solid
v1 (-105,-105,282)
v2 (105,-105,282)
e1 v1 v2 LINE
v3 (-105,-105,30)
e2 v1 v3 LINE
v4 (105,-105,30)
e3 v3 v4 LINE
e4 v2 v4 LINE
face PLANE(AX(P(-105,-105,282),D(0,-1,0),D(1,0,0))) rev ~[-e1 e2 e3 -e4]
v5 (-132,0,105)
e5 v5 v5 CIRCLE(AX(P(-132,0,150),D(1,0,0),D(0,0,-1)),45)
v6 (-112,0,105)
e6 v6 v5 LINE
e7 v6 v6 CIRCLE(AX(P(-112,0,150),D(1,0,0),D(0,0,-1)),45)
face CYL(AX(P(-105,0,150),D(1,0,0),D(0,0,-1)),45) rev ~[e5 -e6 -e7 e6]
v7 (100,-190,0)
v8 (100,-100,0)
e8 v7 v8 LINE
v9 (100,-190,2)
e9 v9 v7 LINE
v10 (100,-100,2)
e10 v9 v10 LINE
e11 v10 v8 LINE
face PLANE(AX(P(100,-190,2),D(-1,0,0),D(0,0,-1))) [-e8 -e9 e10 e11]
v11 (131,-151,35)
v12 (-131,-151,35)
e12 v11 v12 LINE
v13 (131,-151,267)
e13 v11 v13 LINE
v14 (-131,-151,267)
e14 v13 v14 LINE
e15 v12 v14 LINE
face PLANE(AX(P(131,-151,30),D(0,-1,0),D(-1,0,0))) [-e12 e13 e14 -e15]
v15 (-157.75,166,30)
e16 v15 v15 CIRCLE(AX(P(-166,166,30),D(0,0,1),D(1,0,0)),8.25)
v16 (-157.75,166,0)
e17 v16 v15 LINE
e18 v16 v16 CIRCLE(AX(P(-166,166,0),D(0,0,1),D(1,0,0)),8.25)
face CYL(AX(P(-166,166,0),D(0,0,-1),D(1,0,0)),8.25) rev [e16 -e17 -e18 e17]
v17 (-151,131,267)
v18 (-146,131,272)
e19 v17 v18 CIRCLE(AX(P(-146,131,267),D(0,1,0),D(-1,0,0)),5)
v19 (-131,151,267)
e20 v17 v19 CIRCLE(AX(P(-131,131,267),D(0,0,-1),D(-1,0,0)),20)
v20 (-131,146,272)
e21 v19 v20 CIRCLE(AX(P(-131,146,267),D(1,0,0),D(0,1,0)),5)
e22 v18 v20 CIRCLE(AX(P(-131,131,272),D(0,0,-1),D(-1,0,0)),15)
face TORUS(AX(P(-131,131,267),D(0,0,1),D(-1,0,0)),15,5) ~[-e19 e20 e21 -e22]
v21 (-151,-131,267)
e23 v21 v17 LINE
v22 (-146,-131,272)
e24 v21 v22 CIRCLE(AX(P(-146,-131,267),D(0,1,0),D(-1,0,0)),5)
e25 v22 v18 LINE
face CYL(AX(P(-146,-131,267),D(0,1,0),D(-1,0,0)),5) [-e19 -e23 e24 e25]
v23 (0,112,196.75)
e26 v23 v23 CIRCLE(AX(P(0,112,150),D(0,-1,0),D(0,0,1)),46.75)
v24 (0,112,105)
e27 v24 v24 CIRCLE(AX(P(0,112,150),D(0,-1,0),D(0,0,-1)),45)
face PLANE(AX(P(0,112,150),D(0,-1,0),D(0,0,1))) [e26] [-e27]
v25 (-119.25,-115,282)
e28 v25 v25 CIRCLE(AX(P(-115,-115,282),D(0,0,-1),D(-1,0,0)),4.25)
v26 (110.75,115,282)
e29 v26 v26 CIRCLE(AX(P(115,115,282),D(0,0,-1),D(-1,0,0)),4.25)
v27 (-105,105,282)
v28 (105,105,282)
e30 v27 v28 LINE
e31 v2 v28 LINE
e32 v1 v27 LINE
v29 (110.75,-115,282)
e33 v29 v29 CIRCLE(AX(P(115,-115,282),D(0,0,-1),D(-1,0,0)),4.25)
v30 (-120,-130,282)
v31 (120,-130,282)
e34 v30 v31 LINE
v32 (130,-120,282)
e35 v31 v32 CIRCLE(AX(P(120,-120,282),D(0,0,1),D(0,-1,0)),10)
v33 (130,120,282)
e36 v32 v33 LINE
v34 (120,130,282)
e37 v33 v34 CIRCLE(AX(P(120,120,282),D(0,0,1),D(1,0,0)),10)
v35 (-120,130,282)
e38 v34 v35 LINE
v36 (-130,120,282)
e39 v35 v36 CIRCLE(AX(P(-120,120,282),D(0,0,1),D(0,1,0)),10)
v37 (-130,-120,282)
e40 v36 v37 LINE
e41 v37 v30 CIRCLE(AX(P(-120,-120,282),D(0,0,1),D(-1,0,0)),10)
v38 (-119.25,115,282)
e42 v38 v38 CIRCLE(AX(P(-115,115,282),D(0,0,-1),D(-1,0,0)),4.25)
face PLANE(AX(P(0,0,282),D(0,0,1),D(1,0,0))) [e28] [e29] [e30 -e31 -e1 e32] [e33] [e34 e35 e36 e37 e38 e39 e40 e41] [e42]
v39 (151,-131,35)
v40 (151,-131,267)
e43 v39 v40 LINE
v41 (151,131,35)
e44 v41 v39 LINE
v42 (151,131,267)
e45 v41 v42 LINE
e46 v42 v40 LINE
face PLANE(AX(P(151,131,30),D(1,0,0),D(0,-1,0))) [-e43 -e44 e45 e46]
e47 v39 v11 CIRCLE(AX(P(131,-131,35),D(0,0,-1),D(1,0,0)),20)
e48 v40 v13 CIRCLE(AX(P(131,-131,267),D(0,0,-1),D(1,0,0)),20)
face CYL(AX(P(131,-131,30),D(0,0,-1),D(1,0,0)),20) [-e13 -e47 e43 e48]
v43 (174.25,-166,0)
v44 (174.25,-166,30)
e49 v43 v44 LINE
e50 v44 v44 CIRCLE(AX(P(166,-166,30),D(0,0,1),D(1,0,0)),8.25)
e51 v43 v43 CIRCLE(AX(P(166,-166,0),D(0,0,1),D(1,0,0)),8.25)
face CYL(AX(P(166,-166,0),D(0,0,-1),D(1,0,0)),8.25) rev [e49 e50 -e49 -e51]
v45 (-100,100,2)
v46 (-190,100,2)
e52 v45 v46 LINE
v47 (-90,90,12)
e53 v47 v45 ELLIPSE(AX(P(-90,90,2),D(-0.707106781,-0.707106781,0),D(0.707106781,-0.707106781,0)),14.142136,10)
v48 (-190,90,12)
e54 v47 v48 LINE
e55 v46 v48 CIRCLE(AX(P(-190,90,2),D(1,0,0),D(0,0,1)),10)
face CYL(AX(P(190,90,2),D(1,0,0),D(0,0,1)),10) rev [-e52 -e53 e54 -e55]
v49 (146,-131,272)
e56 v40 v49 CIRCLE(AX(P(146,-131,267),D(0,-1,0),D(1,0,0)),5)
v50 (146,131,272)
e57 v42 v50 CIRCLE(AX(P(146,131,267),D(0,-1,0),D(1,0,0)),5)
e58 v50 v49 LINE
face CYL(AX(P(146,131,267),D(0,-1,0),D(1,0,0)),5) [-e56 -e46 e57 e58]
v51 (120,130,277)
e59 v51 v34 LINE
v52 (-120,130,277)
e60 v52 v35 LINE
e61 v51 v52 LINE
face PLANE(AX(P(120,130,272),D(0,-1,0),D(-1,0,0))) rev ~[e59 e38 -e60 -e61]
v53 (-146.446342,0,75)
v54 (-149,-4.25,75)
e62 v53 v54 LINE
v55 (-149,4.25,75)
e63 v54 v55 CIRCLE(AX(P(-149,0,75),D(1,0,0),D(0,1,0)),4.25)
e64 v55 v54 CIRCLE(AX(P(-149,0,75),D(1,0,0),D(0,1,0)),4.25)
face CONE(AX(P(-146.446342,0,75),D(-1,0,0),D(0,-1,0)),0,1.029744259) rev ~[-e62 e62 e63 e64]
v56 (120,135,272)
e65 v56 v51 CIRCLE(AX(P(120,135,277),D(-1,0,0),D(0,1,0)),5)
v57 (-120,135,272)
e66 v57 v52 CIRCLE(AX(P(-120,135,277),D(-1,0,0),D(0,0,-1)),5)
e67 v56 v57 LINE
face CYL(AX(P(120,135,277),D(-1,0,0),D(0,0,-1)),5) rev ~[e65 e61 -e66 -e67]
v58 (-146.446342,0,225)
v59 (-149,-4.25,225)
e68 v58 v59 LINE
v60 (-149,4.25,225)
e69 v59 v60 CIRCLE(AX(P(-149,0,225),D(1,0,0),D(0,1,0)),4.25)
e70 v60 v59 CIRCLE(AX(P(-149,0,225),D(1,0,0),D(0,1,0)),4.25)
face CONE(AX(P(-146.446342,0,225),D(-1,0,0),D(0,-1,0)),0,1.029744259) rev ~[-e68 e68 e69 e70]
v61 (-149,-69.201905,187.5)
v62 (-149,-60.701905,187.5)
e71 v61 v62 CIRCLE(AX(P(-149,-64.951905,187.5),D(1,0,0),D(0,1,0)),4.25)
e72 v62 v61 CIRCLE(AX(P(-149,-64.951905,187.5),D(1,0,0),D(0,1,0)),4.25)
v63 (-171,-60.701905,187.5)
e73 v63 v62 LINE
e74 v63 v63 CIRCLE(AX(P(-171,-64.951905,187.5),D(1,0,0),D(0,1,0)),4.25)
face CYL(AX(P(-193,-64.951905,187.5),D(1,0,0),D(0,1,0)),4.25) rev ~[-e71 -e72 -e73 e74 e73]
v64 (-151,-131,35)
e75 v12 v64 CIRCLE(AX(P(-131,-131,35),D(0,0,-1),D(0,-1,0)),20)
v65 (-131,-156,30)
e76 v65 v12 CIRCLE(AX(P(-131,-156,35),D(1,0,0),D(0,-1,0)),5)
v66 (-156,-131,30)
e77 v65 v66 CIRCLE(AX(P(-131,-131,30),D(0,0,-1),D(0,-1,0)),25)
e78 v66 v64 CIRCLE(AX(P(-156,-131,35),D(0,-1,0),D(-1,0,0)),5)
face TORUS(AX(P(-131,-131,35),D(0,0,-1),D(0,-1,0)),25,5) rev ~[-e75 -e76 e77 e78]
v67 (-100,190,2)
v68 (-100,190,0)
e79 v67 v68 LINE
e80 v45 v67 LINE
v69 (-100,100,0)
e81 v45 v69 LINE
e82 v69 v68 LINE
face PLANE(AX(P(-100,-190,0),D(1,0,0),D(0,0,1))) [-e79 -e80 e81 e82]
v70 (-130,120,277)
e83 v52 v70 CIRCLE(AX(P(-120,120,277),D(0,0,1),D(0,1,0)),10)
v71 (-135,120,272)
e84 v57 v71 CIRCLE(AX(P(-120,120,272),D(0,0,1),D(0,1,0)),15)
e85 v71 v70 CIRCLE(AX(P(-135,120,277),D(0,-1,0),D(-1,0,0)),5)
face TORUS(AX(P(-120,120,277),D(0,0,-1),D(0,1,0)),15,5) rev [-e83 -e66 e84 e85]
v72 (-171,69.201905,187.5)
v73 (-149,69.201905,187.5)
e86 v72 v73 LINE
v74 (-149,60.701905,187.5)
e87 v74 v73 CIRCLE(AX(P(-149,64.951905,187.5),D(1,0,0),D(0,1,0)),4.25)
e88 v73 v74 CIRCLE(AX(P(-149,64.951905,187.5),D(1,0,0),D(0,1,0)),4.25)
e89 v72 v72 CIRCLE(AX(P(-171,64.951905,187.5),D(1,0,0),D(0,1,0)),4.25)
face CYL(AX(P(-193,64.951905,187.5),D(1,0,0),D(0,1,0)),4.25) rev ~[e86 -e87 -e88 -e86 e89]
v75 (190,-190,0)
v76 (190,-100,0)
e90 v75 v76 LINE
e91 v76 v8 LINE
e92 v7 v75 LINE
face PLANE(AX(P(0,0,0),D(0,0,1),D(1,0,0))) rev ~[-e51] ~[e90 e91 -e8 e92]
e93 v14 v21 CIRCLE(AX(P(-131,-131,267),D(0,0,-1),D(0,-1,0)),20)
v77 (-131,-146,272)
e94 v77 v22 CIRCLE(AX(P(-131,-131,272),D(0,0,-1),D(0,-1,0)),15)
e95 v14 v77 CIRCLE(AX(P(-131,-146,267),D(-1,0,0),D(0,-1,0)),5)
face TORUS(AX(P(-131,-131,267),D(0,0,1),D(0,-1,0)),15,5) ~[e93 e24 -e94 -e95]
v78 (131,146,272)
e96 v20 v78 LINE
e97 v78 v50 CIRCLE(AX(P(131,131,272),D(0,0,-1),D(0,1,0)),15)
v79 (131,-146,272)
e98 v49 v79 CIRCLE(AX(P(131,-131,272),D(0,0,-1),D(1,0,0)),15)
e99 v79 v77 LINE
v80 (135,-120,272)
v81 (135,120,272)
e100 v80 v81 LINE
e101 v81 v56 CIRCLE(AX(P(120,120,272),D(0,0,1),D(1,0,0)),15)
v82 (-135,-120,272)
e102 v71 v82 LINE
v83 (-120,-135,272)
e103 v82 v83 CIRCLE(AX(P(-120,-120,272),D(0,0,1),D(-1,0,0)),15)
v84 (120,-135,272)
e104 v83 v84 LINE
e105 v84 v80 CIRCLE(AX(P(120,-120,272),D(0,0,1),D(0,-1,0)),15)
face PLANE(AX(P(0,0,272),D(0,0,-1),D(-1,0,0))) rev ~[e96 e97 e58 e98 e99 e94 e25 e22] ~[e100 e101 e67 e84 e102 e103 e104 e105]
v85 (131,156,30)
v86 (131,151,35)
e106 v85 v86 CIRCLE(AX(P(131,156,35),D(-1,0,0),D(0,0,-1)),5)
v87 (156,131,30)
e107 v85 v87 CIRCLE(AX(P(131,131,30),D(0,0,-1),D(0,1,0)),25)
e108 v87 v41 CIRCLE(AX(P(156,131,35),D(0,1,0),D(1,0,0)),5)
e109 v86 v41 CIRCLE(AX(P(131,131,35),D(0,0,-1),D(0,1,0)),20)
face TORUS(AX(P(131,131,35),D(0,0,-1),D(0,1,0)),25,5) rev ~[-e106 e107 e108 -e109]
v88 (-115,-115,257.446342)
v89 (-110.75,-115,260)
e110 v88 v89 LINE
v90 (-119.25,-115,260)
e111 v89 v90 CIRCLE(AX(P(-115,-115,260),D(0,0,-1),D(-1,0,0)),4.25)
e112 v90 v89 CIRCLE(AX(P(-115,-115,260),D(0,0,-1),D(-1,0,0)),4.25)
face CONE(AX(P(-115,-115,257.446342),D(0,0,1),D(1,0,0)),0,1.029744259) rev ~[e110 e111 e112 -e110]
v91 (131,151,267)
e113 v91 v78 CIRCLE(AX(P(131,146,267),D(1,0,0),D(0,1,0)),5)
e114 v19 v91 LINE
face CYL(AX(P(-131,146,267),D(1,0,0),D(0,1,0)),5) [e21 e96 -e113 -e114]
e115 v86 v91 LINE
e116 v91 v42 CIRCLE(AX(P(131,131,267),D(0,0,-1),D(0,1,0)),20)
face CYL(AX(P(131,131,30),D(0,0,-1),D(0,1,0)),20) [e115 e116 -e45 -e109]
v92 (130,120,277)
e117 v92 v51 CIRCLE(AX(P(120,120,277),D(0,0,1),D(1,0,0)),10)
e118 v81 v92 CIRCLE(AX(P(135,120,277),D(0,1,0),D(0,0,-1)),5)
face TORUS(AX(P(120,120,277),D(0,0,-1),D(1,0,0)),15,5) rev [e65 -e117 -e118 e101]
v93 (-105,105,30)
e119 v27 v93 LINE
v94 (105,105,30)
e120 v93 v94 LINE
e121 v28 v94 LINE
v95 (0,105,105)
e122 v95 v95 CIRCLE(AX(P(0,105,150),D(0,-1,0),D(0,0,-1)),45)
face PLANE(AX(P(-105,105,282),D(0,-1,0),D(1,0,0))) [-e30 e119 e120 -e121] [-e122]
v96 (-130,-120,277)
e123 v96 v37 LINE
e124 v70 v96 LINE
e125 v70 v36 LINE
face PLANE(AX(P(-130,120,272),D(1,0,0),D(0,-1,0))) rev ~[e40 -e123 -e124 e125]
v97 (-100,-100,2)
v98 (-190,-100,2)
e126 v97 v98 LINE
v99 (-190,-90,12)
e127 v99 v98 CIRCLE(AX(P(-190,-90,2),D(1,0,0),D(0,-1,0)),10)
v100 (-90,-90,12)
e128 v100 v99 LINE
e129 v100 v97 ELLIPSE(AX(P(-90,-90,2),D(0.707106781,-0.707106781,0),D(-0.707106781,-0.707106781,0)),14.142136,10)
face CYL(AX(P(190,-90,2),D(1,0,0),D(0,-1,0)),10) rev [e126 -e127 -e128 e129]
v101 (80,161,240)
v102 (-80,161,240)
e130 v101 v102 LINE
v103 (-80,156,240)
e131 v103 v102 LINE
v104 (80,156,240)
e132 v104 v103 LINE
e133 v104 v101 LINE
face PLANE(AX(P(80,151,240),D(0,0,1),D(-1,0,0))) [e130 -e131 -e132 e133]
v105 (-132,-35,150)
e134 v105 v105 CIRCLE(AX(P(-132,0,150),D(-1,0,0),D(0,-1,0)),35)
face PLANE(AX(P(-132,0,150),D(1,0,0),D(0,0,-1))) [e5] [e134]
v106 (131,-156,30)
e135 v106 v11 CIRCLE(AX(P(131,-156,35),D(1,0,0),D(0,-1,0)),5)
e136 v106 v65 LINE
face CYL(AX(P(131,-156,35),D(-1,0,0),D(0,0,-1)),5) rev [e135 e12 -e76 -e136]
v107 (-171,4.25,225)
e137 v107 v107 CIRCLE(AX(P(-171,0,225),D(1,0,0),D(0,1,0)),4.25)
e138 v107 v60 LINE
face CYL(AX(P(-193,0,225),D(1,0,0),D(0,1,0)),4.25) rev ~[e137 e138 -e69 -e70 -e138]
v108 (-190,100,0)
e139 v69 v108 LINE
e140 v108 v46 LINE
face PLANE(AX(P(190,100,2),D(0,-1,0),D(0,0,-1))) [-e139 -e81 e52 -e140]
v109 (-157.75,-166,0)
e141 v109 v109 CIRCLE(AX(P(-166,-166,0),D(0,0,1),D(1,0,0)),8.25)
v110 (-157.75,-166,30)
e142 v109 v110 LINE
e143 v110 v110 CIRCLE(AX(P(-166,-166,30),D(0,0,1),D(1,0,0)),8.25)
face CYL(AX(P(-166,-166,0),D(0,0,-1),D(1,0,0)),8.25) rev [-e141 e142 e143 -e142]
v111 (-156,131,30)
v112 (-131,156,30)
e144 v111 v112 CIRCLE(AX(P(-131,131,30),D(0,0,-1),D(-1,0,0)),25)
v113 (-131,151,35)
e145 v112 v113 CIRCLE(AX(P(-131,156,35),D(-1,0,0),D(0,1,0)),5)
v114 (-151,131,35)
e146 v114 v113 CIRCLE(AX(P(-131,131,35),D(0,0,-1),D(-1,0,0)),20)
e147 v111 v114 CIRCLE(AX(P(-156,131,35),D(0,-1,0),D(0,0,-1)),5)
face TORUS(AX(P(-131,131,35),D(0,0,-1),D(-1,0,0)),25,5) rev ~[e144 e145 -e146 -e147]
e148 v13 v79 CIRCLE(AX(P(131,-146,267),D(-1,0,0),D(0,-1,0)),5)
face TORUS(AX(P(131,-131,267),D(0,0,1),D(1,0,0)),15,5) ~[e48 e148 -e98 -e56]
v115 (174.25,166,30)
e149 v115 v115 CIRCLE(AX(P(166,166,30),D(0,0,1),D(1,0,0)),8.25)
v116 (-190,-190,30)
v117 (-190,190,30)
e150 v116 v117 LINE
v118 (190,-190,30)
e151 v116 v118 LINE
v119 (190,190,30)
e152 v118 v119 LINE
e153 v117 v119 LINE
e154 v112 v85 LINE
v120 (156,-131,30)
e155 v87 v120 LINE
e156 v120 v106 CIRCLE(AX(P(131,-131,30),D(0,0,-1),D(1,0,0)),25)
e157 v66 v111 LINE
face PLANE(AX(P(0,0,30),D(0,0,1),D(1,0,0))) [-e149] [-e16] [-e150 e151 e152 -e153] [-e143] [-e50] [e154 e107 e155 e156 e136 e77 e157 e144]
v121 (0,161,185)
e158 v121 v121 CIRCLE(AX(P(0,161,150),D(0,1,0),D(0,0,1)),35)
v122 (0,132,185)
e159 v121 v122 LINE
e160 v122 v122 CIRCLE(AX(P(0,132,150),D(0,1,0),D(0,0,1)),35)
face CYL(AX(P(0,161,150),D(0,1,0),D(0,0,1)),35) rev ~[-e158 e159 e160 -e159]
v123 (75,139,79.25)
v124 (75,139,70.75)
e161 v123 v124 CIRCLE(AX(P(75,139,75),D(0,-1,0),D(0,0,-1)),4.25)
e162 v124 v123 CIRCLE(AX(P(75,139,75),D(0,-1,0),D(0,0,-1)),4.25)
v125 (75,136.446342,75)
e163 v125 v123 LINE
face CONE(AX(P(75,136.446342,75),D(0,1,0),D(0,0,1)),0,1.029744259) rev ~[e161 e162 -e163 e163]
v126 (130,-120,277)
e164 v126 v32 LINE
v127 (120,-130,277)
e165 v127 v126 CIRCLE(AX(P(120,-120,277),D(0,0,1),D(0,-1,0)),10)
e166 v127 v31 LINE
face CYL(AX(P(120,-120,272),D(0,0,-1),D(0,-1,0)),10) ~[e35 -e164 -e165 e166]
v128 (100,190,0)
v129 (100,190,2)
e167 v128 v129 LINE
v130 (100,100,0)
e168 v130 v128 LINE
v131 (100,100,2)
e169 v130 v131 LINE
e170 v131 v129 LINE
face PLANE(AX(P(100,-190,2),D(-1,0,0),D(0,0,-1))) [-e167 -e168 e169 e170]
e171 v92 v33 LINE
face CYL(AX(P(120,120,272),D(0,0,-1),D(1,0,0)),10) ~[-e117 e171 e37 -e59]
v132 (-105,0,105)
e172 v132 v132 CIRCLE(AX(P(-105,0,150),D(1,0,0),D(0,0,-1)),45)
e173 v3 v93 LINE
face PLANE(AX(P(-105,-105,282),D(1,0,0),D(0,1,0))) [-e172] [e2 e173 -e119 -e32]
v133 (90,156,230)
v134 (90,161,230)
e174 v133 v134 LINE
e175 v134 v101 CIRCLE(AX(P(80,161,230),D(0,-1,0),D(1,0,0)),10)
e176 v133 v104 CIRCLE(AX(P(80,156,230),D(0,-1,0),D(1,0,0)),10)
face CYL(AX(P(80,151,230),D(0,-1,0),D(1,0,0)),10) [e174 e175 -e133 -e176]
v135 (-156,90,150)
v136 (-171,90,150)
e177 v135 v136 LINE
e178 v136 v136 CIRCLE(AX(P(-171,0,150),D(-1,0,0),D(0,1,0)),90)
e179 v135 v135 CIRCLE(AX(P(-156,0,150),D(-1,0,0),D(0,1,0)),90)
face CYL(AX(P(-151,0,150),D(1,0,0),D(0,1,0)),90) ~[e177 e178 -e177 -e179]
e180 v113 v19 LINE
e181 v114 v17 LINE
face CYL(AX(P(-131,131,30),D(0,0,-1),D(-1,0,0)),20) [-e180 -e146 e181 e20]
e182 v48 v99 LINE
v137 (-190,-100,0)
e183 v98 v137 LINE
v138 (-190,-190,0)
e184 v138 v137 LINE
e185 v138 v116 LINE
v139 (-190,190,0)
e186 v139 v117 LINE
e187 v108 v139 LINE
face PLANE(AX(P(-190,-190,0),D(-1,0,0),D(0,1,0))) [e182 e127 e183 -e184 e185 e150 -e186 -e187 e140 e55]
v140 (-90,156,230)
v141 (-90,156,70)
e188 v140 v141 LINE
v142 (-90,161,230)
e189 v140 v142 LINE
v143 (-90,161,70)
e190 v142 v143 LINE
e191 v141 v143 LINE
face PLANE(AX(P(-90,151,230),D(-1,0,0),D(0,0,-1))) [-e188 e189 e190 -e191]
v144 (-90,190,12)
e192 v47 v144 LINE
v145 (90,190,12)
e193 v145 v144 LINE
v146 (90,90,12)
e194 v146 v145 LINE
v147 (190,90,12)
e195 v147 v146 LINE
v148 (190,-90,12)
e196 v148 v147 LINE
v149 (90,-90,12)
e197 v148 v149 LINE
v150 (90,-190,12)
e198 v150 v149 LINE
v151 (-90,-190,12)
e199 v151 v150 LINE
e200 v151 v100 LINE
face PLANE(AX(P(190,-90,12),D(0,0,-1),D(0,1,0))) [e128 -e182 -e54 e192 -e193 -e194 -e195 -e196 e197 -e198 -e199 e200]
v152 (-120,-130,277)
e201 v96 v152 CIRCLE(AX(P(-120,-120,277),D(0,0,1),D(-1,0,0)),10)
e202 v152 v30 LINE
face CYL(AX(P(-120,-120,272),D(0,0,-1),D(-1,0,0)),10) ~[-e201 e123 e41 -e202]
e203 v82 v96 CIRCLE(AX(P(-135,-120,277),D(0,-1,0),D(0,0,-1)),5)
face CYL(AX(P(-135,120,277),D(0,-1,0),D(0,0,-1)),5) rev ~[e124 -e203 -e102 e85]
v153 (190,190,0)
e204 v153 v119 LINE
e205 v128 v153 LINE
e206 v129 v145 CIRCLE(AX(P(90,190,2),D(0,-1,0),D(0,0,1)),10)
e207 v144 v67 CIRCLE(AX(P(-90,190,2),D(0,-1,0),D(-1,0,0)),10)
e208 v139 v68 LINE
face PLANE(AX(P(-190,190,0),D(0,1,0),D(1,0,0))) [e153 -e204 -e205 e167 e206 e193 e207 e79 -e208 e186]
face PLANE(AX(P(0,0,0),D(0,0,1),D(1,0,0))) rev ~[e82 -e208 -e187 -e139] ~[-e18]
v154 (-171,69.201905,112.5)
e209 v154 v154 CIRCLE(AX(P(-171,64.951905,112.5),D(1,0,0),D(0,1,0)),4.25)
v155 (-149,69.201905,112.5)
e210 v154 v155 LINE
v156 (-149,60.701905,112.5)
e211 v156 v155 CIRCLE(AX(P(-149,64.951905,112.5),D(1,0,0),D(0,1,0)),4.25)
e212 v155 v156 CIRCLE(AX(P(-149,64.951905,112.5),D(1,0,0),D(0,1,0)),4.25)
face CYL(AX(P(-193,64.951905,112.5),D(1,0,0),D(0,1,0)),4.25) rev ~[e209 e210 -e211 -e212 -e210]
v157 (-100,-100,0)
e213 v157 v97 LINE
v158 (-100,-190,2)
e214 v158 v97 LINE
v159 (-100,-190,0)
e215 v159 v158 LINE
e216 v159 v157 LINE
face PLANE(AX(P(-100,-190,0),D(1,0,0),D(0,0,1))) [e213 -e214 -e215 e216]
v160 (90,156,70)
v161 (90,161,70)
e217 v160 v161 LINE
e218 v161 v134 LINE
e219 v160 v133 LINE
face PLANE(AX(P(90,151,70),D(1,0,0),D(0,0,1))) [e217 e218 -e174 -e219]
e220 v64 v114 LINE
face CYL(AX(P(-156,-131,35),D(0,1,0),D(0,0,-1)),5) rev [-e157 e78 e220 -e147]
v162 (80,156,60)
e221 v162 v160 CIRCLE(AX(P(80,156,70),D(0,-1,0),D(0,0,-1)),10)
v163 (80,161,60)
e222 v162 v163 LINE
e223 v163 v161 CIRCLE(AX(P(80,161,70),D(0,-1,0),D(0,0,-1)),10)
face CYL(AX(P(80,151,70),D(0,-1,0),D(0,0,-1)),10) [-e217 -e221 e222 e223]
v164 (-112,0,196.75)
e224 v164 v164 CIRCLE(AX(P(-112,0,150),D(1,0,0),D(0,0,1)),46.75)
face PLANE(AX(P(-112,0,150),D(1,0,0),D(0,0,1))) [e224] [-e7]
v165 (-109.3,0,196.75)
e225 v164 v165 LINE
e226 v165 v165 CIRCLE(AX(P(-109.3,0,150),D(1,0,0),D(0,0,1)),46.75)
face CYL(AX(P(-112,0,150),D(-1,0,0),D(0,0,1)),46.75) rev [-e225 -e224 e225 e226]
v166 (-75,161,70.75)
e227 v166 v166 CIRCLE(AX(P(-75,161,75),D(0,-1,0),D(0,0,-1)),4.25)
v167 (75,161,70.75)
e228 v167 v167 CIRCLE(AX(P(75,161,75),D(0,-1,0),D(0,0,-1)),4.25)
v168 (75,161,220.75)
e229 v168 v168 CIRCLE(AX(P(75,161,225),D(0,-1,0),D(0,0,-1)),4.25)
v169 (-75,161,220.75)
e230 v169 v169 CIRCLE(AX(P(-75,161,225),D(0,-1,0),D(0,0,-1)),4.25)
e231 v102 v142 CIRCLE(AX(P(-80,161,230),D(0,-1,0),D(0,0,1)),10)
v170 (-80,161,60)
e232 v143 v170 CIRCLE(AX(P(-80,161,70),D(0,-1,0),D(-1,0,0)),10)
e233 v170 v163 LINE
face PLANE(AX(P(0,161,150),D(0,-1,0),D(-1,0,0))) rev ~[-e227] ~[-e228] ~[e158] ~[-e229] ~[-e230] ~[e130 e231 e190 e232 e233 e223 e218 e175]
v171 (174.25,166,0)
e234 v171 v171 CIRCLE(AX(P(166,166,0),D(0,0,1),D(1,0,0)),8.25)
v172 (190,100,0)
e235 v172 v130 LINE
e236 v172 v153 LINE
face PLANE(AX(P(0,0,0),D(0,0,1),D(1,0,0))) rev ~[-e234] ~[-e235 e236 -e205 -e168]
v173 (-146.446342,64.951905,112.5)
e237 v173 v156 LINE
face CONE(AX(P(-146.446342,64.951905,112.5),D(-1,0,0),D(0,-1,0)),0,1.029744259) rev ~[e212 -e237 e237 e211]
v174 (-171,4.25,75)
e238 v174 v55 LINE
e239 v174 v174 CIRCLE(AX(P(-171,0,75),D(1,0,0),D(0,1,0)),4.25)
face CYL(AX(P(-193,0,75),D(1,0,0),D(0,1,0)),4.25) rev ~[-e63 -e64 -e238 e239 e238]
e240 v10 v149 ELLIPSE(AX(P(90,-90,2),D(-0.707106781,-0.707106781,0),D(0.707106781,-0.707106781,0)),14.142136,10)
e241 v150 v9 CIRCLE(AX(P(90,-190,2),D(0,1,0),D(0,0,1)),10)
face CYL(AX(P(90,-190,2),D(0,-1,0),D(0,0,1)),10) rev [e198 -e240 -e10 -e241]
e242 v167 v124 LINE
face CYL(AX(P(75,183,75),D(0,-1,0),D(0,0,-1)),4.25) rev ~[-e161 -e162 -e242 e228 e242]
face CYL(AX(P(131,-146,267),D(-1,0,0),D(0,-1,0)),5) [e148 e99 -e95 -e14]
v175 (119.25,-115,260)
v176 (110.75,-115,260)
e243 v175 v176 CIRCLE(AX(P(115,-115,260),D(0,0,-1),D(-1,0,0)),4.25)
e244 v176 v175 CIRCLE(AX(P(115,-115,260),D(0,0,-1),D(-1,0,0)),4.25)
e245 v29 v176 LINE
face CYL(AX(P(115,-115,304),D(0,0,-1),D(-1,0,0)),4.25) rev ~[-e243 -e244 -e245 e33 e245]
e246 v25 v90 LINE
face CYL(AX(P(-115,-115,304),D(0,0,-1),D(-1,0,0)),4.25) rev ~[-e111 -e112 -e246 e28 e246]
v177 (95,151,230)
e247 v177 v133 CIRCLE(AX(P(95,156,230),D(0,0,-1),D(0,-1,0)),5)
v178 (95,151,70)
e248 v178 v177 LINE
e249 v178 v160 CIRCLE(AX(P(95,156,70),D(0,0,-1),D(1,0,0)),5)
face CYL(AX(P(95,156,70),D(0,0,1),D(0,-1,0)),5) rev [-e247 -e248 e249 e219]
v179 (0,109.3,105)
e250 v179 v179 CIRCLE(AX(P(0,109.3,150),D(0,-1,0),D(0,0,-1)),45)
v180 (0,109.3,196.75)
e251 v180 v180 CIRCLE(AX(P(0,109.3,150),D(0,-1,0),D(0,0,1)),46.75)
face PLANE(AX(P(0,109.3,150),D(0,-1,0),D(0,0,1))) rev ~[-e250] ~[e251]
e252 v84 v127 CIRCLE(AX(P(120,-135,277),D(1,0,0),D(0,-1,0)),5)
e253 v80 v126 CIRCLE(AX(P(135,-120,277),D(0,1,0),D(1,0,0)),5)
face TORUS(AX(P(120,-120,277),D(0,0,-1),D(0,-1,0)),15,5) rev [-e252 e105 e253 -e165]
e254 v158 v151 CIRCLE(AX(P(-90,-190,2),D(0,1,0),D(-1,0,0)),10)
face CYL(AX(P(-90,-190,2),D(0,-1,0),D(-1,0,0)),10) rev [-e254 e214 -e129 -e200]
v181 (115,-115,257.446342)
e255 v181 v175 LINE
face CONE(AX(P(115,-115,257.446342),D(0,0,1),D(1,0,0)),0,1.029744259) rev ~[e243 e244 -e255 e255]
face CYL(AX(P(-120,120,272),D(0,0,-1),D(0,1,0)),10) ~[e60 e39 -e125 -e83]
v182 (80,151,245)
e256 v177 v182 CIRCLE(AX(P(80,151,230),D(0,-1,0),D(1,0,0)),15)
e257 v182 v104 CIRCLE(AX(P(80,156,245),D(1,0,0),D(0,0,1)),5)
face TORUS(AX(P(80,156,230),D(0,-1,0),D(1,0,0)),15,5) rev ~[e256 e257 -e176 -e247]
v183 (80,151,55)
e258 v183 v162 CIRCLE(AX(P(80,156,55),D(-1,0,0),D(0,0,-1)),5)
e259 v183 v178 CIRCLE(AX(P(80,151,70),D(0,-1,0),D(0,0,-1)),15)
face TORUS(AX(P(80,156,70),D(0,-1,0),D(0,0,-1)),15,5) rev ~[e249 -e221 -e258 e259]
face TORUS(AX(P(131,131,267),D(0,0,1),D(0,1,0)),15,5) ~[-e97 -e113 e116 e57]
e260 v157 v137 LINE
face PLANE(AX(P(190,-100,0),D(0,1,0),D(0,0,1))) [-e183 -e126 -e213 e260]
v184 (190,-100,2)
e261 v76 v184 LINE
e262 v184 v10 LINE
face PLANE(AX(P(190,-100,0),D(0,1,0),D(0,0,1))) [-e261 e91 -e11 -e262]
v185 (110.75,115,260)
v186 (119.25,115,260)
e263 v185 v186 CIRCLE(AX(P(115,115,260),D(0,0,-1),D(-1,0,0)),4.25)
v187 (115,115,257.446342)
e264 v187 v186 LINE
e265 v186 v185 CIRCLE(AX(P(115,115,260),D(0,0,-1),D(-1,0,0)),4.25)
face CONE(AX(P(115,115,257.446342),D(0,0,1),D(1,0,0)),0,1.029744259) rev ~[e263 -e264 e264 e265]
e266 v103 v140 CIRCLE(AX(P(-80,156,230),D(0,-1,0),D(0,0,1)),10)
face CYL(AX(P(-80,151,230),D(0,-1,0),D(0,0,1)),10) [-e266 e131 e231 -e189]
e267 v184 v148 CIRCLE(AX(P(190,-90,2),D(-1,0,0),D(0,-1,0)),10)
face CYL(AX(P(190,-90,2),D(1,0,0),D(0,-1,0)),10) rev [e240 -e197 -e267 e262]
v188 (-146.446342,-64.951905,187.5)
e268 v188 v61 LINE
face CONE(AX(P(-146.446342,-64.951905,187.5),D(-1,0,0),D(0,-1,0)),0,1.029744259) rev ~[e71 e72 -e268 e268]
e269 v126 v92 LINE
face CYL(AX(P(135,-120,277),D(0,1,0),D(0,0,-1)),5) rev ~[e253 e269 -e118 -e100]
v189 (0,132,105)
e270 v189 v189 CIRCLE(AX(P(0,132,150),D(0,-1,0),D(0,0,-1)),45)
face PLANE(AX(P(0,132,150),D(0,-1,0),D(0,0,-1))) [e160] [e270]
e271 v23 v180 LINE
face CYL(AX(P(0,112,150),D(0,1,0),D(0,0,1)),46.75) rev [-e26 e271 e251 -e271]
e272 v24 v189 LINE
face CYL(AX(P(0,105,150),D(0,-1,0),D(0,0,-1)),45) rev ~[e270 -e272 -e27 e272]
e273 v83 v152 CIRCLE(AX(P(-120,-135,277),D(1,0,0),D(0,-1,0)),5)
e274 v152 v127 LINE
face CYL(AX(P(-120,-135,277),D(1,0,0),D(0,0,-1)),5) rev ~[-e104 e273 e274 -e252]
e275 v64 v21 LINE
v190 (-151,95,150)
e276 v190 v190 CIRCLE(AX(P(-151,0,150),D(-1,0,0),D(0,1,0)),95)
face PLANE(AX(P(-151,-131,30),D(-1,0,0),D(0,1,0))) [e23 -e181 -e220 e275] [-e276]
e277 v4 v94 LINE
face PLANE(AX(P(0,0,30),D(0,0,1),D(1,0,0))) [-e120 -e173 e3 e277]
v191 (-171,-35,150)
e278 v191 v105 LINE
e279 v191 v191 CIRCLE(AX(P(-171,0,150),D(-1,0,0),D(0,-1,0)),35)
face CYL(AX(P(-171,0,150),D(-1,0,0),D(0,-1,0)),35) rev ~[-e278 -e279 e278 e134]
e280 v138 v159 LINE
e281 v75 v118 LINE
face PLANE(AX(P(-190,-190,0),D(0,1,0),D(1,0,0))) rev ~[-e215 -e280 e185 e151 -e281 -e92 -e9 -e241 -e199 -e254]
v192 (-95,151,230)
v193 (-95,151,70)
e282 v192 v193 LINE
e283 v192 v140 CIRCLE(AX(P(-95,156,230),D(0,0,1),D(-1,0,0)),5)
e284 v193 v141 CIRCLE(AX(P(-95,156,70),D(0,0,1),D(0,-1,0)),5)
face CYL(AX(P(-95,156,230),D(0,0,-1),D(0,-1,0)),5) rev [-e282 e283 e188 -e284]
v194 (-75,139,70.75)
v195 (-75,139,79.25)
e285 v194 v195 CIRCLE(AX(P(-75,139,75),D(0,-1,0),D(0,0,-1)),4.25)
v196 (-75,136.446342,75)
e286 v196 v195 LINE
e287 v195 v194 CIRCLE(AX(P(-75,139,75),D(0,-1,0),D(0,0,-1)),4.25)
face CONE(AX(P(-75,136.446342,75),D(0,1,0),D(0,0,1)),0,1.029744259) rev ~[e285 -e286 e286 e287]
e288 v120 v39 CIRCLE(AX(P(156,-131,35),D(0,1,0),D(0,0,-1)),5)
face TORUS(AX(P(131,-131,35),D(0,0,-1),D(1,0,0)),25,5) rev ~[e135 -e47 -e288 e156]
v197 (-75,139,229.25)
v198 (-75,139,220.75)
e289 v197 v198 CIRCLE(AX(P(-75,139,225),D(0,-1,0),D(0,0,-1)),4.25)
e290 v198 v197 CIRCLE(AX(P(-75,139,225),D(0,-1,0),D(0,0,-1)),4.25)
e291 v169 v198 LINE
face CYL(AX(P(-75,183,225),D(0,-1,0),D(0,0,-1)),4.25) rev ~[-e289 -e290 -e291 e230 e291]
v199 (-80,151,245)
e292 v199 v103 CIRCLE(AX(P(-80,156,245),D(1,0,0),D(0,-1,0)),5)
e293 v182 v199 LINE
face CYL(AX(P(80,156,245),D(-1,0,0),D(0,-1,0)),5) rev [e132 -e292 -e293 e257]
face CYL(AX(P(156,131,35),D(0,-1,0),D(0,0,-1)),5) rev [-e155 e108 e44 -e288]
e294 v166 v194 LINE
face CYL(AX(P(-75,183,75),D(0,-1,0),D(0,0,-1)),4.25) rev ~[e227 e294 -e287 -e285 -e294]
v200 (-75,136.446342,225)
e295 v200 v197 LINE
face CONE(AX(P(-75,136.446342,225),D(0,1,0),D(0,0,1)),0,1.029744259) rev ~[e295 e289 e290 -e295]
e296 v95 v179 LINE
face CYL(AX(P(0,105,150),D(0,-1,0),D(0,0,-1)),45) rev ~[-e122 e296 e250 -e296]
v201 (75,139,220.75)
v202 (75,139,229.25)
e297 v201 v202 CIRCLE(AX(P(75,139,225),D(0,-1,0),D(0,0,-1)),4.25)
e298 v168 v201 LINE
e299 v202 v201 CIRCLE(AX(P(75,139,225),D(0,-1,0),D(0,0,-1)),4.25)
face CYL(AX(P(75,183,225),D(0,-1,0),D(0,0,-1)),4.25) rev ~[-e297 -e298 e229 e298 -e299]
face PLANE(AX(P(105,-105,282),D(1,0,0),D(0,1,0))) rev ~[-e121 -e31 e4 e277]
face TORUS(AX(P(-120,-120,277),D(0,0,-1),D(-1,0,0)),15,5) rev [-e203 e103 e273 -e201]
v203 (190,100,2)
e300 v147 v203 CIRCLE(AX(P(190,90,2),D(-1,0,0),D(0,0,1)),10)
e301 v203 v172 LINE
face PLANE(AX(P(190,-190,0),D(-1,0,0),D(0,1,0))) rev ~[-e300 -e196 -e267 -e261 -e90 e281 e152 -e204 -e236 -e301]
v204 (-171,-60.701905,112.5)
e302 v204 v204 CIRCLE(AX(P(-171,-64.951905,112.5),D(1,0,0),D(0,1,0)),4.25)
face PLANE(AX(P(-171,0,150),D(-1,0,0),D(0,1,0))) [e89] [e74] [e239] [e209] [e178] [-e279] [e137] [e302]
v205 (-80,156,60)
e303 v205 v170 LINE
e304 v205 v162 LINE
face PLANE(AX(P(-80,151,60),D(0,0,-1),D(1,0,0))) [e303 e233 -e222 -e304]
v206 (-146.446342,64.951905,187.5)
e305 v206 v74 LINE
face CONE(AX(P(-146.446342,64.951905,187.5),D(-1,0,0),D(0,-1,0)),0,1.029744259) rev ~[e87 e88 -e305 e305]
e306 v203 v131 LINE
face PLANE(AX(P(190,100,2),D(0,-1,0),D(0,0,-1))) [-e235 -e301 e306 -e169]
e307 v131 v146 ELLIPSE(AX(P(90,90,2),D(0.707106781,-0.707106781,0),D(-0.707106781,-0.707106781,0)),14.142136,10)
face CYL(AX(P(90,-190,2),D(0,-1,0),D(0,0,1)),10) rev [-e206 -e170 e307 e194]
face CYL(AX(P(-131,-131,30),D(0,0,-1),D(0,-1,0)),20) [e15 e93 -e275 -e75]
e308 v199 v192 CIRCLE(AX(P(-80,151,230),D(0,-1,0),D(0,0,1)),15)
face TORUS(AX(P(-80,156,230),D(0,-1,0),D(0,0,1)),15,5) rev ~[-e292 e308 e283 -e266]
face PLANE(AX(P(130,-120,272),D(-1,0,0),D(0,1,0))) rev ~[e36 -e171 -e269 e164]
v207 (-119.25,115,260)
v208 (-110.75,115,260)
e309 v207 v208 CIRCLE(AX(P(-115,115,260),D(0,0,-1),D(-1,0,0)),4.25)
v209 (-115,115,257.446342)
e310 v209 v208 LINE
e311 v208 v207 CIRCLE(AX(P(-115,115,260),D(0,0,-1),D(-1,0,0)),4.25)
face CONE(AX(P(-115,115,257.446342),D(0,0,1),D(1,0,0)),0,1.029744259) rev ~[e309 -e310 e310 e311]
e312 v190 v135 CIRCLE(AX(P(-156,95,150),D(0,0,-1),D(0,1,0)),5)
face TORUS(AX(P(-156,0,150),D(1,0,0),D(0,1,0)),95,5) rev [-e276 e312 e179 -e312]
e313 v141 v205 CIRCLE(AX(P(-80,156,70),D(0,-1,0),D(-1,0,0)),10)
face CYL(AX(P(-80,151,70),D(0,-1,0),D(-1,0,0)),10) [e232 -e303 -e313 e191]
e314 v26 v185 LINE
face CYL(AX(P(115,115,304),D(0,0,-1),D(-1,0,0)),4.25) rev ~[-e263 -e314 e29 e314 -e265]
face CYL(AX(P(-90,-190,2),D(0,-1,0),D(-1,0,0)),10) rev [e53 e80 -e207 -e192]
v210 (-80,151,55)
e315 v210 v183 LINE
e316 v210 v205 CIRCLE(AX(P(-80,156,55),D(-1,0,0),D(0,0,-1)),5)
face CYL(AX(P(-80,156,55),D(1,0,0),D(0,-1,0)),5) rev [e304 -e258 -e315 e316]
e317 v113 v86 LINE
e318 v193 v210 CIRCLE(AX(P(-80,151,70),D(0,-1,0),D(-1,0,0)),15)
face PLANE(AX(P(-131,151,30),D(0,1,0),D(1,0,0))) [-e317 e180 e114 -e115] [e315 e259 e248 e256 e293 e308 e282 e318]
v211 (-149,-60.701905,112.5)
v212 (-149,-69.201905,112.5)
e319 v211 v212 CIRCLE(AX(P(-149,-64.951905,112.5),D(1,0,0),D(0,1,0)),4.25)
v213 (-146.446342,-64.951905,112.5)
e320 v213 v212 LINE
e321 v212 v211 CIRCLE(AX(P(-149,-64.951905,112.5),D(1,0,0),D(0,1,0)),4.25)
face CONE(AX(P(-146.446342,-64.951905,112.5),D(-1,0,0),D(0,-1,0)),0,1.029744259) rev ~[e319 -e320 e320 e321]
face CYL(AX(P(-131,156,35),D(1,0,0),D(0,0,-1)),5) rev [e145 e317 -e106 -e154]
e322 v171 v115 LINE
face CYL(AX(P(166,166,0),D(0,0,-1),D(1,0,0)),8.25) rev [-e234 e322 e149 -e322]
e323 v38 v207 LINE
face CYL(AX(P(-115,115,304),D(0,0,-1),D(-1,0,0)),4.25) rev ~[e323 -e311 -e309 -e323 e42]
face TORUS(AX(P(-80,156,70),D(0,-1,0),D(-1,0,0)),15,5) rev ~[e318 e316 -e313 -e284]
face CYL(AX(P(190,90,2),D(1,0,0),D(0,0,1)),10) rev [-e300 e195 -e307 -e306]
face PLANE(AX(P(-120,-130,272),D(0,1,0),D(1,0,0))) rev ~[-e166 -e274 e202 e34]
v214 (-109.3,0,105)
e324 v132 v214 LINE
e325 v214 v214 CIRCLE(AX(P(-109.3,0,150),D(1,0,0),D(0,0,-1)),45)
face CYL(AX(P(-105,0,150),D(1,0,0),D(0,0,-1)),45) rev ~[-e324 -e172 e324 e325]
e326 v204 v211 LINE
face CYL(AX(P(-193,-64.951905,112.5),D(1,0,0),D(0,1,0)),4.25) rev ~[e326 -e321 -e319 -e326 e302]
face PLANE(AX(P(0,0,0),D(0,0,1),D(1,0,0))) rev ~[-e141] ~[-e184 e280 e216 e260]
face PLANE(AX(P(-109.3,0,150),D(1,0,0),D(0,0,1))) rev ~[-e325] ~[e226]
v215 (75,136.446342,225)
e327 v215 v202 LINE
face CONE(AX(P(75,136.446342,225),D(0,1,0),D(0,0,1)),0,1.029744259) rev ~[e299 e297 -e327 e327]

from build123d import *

# Parameters (mm, degrees)
SKETCH_1_W              = 380
SKETCH_1_H              = 380
SKETCH_1_R              = 8.25
EXTRUDE_1_DEPTH         = 30
CUT_EXTRUDE_1_DEPTH     = 426.910788781
CUT_EXTRUDE_2_DEPTH     = 426.910788781
EXTRUDE_2_DEPTH         = 242
EXTRUDE_3_DEPTH         = 10
EXTRUDE_5_DEPTH         = 10
HOLE_WIZARD_M10_1_D     = 8.5
HOLE_WIZARD_M10_1_DEPTH = 22
HOLE_WIZARD_M10_1_TIP   = 2.553657631
HOLE_WIZARD_M10_3_D     = 8.5
HOLE_WIZARD_M10_3_DEPTH = 22
HOLE_WIZARD_M10_3_TIP   = 2.553657631
SKETCH_14_W             = 210
SKETCH_14_H             = 210
CUT_EXTRUDE_3_DEPTH     = 252
SKETCH_15_R             = 90
EXTRUDE_6_DEPTH         = 20
FILLET_1_R              = 5
CUT_EXTRUDE_4_REACH     = 490.697
SKETCH_18_R             = 35
CUT_EXTRUDE_5_REACH     = 497.928
SKETCH_19_R             = 35
SKETCH_20_R             = 45
CUT_EXTRUDE_6_DEPTH     = 27
SKETCH_21_R             = 45
CUT_EXTRUDE_7_DEPTH     = 27
HOLE_WIZARD_M10_4_D     = 8.5
HOLE_WIZARD_M10_4_DEPTH = 22
HOLE_WIZARD_M10_4_TIP   = 2.553657631
FILLET_2_R              = 5
SKETCH_24_R             = 46.75
CUT_EXTRUDE_8_DEPTH     = 2.7
SKETCH_25_R             = 46.75
CUT_EXTRUDE_9_DEPTH     = 2.7


with BuildPart() as part:
    # 草图1 → 凸台-拉伸1 (new body)
    with BuildSketch(Plane.XY):
        Rectangle(SKETCH_1_W, SKETCH_1_H)
        with Locations((-166, 166)):
            Circle(SKETCH_1_R, mode=Mode.SUBTRACT)
        with Locations((166, 166)):
            Circle(SKETCH_1_R, mode=Mode.SUBTRACT)
        with Locations((166, -166)):
            Circle(SKETCH_1_R, mode=Mode.SUBTRACT)
        with Locations((-166, -166)):
            Circle(SKETCH_1_R, mode=Mode.SUBTRACT)
    extrude(amount=EXTRUDE_1_DEPTH)

    # 草图2 → 切除-拉伸1 (cut, through all)
    with BuildSketch(Plane.XZ.offset(190)):
        with BuildLine():
            Line((-100, 0), (-100, 2))
            ThreePointArc((-100, 2), (-97.071067812, 9.071067812), (-90, 12))
            Line((-90, 12), (90, 12))
            ThreePointArc((90, 12), (97.071067812, 9.071067812), (100, 2))
            Line((100, 2), (100, 0))
            Line((100, 0), (-100, 0))
        make_face()
    extrude(amount=-CUT_EXTRUDE_1_DEPTH, mode=Mode.SUBTRACT)

    # 草图3 → 切除-拉伸2 (cut, through all)
    with BuildSketch(Plane(origin=(190, 0, 0), x_dir=(0, 0, -1), z_dir=(1, 0, 0))):
        with BuildLine():
            Line((0, -100), (-2, -100))
            ThreePointArc((-2, -100), (-9.071067812, -97.071067812), (-12, -90))
            Line((-12, -90), (-12, 90))
            ThreePointArc((-12, 90), (-9.071067812, 97.071067812), (-2, 100))
            Line((-2, 100), (0, 100))
            Line((0, 100), (0, -100))
        make_face()
    extrude(amount=-CUT_EXTRUDE_2_DEPTH, mode=Mode.SUBTRACT)

    # 草图4 → 凸台-拉伸2 (add)
    with BuildSketch(Plane.XY.offset(30)):
        with BuildLine():
            Line((-131, 151), (131, 151))
            ThreePointArc((131, 151), (145.142135624, 145.142135624), (151, 131))
            Line((151, 131), (151, -131))
            ThreePointArc((151, -131), (145.142135624, -145.142135624), (131, -151))
            Line((131, -151), (-131, -151))
            ThreePointArc((-131, -151), (-145.142135624, -145.142135624), (-151, -131))
            Line((-151, -131), (-151, 131))
            ThreePointArc((-151, 131), (-145.142135624, 145.142135624), (-131, 151))
        make_face()
    extrude(amount=EXTRUDE_2_DEPTH)

    # 草图5 → 凸台-拉伸3 (add)
    with BuildSketch(Plane(origin=(0, 151, 0), x_dir=(1, 0, 0), z_dir=(0, 1, 0))):
        with BuildLine():
            Line((80, -240), (-80, -240))
            ThreePointArc((-80, -240), (-87.071067812, -237.071067812), (-90, -230))
            Line((-90, -230), (-90, -70))
            ThreePointArc((-90, -70), (-87.071067812, -62.928932188), (-80, -60))
            Line((-80, -60), (80, -60))
            ThreePointArc((80, -60), (87.071067812, -62.928932188), (90, -70))
            Line((90, -70), (90, -230))
            ThreePointArc((90, -230), (87.071067812, -237.071067812), (80, -240))
        make_face()
    extrude(amount=EXTRUDE_3_DEPTH)

    # 草图7 → 凸台-拉伸5 (add)
    with BuildSketch(Plane.XY.offset(272)):
        with BuildLine():
            Line((-120, -130), (120, -130))
            ThreePointArc((120, -130), (127.071067812, -127.071067812), (130, -120))
            Line((130, -120), (130, 120))
            ThreePointArc((130, 120), (127.071067812, 127.071067812), (120, 130))
            Line((120, 130), (-120, 130))
            ThreePointArc((-120, 130), (-127.071067812, 127.071067812), (-130, 120))
            Line((-130, 120), (-130, -120))
            ThreePointArc((-130, -120), (-127.071067812, -127.071067812), (-120, -130))
        make_face()
    extrude(amount=EXTRUDE_5_DEPTH)

    # M10 螺纹孔1
    with Locations(Plane(origin=(75, 161, 225), x_dir=(0, 0, 1), z_dir=(0, 1, 0))):
        with Locations((0, 0), (0, -150), (-150, -150), (-150, 0)):
            Hole(HOLE_WIZARD_M10_1_D / 2, depth=HOLE_WIZARD_M10_1_DEPTH)
            with Locations((0, 0, -(HOLE_WIZARD_M10_1_DEPTH + HOLE_WIZARD_M10_1_TIP / 2))):  # 118° drill point
                Cone(0, HOLE_WIZARD_M10_1_D / 2, HOLE_WIZARD_M10_1_TIP, mode=Mode.SUBTRACT)

    # M10 螺纹孔3
    with Locations(Plane(origin=(115, -115, 282), x_dir=(1, 0, 0), z_dir=(0, 0, 1))):
        with Locations((0, 0), (0, 230), (-230, 230), (-230, 0)):
            Hole(HOLE_WIZARD_M10_3_D / 2, depth=HOLE_WIZARD_M10_3_DEPTH)
            with Locations((0, 0, -(HOLE_WIZARD_M10_3_DEPTH + HOLE_WIZARD_M10_3_TIP / 2))):  # 118° drill point
                Cone(0, HOLE_WIZARD_M10_3_D / 2, HOLE_WIZARD_M10_3_TIP, mode=Mode.SUBTRACT)

    # 草图14 → 切除-拉伸3 (cut)
    with BuildSketch(Plane.XY.offset(282)):
        Rectangle(SKETCH_14_W, SKETCH_14_H)
    extrude(amount=-CUT_EXTRUDE_3_DEPTH, mode=Mode.SUBTRACT)

    # 草图15 → 凸台-拉伸6 (add)
    with BuildSketch(Plane.ZY.offset(151)):
        with Locations(Location((150, 0, 0), (0, 0, 90))):
            Circle(SKETCH_15_R)
    extrude(amount=EXTRUDE_6_DEPTH)

    # 圆角1
    fillet_1_edges = [part.edges().sort_by_distance(p)[0] for p in [
        (-145.142135624, -145.142135624, 30),
        (0, -151, 30),
        (145.142135624, -145.142135624, 30),
        (151, 0, 30),
        (145.142135624, 145.142135624, 30),
        (0, 151, 30),
        (-145.142135624, 145.142135624, 30),
        (-151, 0, 30),
        (-145.142135624, -145.142135624, 272),
        (0, -151, 272),
        (145.142135624, -145.142135624, 272),
        (151, 0, 272),
        (145.142135624, 145.142135624, 272),
        (0, 151, 272),
        (-145.142135624, 145.142135624, 272),
        (-151, 0, 272),
        (87.071067812, 151, 62.928932188),
        (0, 151, 60),
        (-87.071067812, 151, 62.928932188),
        (-90, 151, 150),
        (-87.071067812, 151, 237.071067812),
        (0, 151, 240),
        (87.071067812, 151, 237.071067812),
        (90, 151, 150),
        (127.071067812, -127.071067812, 272),
        (130, 0, 272),
        (127.071067812, 127.071067812, 272),
        (0, 130, 272),
        (-127.071067812, 127.071067812, 272),
        (-130, 0, 272),
        (-127.071067812, -127.071067812, 272),
        (0, -130, 272),
    ]]
    fillet(fillet_1_edges, radius=FILLET_1_R)

    # 草图18 → 切除-拉伸4 (cut, up to next)
    with BuildSketch(Plane(origin=(0, 161, 0), x_dir=(1, 0, 0), z_dir=(0, 1, 0)), mode=Mode.PRIVATE) as cut_extrude_4_sk1:
        with Locations(Location((0, -150, 0), (0, 0, 270))):
            Circle(SKETCH_18_R)
    cut_extrude_4_tool1 = extrude(cut_extrude_4_sk1.sketch, amount=-CUT_EXTRUDE_4_REACH, mode=Mode.PRIVATE) & part.part
    add(cut_extrude_4_tool1.solids().sort_by_distance((0, 161, 150))[0], mode=Mode.SUBTRACT)

    # 草图19 → 切除-拉伸5 (cut, up to next)
    with BuildSketch(Plane.ZY.offset(171), mode=Mode.PRIVATE) as cut_extrude_5_sk1:
        with Locations(Location((150, 0, 0), (0, 0, 270))):
            Circle(SKETCH_19_R)
    cut_extrude_5_tool1 = extrude(cut_extrude_5_sk1.sketch, amount=-CUT_EXTRUDE_5_REACH, mode=Mode.PRIVATE) & part.part
    add(cut_extrude_5_tool1.solids().sort_by_distance((-171, 0, 150))[0], mode=Mode.SUBTRACT)

    # 草图20 → 切除-拉伸6 (cut)
    with BuildSketch(Plane.XZ.offset(-105)):
        with Locations(Location((0, 150, 0), (0, 0, 270))):
            Circle(SKETCH_20_R)
    extrude(amount=-CUT_EXTRUDE_6_DEPTH, mode=Mode.SUBTRACT)

    # 草图21 → 切除-拉伸7 (cut)
    with BuildSketch(Plane(origin=(-105, 0, 0), x_dir=(0, 0, -1), z_dir=(1, 0, 0))):
        with Locations((-150, 0)):
            Circle(SKETCH_21_R)
    extrude(amount=-CUT_EXTRUDE_7_DEPTH, mode=Mode.SUBTRACT)

    # M10 螺纹孔4
    with Locations(Plane(origin=(-171, 0, 225), x_dir=(0, -1, 0), z_dir=(-1, 0, 0))):
        with Locations((0, 0), (64.951905284, -37.5), (64.951905284, -112.5), (0, -150), (-64.951905284, -112.5), (-64.951905284, -37.5)):
            Hole(HOLE_WIZARD_M10_4_D / 2, depth=HOLE_WIZARD_M10_4_DEPTH)
            with Locations((0, 0, -(HOLE_WIZARD_M10_4_DEPTH + HOLE_WIZARD_M10_4_TIP / 2))):  # 118° drill point
                Cone(0, HOLE_WIZARD_M10_4_D / 2, HOLE_WIZARD_M10_4_TIP, mode=Mode.SUBTRACT)

    # 圆角2
    fillet_2_edges = [part.edges().sort_by_distance(p)[0] for p in [
        (-151, -90, 150),
    ]]
    fillet(fillet_2_edges, radius=FILLET_2_R)

    # 草图24 → 切除-拉伸8 (cut)
    with BuildSketch(Plane(origin=(-112, 0, 0), x_dir=(0, 0, -1), z_dir=(1, 0, 0))):
        with Locations(Location((-150, 0, 0), (0, 0, 180))):
            Circle(SKETCH_24_R)
    extrude(amount=CUT_EXTRUDE_8_DEPTH, mode=Mode.SUBTRACT)

    # 草图25 → 切除-拉伸9 (cut)
    with BuildSketch(Plane(origin=(0, 112, 0), x_dir=(-1, 0, 0), z_dir=(0, -1, 0))):
        with Locations(Location((0, -150, 0), (0, 0, 270))):
            Circle(SKETCH_25_R)
    extrude(amount=CUT_EXTRUDE_9_DEPTH, mode=Mode.SUBTRACT)


solid = part.part
